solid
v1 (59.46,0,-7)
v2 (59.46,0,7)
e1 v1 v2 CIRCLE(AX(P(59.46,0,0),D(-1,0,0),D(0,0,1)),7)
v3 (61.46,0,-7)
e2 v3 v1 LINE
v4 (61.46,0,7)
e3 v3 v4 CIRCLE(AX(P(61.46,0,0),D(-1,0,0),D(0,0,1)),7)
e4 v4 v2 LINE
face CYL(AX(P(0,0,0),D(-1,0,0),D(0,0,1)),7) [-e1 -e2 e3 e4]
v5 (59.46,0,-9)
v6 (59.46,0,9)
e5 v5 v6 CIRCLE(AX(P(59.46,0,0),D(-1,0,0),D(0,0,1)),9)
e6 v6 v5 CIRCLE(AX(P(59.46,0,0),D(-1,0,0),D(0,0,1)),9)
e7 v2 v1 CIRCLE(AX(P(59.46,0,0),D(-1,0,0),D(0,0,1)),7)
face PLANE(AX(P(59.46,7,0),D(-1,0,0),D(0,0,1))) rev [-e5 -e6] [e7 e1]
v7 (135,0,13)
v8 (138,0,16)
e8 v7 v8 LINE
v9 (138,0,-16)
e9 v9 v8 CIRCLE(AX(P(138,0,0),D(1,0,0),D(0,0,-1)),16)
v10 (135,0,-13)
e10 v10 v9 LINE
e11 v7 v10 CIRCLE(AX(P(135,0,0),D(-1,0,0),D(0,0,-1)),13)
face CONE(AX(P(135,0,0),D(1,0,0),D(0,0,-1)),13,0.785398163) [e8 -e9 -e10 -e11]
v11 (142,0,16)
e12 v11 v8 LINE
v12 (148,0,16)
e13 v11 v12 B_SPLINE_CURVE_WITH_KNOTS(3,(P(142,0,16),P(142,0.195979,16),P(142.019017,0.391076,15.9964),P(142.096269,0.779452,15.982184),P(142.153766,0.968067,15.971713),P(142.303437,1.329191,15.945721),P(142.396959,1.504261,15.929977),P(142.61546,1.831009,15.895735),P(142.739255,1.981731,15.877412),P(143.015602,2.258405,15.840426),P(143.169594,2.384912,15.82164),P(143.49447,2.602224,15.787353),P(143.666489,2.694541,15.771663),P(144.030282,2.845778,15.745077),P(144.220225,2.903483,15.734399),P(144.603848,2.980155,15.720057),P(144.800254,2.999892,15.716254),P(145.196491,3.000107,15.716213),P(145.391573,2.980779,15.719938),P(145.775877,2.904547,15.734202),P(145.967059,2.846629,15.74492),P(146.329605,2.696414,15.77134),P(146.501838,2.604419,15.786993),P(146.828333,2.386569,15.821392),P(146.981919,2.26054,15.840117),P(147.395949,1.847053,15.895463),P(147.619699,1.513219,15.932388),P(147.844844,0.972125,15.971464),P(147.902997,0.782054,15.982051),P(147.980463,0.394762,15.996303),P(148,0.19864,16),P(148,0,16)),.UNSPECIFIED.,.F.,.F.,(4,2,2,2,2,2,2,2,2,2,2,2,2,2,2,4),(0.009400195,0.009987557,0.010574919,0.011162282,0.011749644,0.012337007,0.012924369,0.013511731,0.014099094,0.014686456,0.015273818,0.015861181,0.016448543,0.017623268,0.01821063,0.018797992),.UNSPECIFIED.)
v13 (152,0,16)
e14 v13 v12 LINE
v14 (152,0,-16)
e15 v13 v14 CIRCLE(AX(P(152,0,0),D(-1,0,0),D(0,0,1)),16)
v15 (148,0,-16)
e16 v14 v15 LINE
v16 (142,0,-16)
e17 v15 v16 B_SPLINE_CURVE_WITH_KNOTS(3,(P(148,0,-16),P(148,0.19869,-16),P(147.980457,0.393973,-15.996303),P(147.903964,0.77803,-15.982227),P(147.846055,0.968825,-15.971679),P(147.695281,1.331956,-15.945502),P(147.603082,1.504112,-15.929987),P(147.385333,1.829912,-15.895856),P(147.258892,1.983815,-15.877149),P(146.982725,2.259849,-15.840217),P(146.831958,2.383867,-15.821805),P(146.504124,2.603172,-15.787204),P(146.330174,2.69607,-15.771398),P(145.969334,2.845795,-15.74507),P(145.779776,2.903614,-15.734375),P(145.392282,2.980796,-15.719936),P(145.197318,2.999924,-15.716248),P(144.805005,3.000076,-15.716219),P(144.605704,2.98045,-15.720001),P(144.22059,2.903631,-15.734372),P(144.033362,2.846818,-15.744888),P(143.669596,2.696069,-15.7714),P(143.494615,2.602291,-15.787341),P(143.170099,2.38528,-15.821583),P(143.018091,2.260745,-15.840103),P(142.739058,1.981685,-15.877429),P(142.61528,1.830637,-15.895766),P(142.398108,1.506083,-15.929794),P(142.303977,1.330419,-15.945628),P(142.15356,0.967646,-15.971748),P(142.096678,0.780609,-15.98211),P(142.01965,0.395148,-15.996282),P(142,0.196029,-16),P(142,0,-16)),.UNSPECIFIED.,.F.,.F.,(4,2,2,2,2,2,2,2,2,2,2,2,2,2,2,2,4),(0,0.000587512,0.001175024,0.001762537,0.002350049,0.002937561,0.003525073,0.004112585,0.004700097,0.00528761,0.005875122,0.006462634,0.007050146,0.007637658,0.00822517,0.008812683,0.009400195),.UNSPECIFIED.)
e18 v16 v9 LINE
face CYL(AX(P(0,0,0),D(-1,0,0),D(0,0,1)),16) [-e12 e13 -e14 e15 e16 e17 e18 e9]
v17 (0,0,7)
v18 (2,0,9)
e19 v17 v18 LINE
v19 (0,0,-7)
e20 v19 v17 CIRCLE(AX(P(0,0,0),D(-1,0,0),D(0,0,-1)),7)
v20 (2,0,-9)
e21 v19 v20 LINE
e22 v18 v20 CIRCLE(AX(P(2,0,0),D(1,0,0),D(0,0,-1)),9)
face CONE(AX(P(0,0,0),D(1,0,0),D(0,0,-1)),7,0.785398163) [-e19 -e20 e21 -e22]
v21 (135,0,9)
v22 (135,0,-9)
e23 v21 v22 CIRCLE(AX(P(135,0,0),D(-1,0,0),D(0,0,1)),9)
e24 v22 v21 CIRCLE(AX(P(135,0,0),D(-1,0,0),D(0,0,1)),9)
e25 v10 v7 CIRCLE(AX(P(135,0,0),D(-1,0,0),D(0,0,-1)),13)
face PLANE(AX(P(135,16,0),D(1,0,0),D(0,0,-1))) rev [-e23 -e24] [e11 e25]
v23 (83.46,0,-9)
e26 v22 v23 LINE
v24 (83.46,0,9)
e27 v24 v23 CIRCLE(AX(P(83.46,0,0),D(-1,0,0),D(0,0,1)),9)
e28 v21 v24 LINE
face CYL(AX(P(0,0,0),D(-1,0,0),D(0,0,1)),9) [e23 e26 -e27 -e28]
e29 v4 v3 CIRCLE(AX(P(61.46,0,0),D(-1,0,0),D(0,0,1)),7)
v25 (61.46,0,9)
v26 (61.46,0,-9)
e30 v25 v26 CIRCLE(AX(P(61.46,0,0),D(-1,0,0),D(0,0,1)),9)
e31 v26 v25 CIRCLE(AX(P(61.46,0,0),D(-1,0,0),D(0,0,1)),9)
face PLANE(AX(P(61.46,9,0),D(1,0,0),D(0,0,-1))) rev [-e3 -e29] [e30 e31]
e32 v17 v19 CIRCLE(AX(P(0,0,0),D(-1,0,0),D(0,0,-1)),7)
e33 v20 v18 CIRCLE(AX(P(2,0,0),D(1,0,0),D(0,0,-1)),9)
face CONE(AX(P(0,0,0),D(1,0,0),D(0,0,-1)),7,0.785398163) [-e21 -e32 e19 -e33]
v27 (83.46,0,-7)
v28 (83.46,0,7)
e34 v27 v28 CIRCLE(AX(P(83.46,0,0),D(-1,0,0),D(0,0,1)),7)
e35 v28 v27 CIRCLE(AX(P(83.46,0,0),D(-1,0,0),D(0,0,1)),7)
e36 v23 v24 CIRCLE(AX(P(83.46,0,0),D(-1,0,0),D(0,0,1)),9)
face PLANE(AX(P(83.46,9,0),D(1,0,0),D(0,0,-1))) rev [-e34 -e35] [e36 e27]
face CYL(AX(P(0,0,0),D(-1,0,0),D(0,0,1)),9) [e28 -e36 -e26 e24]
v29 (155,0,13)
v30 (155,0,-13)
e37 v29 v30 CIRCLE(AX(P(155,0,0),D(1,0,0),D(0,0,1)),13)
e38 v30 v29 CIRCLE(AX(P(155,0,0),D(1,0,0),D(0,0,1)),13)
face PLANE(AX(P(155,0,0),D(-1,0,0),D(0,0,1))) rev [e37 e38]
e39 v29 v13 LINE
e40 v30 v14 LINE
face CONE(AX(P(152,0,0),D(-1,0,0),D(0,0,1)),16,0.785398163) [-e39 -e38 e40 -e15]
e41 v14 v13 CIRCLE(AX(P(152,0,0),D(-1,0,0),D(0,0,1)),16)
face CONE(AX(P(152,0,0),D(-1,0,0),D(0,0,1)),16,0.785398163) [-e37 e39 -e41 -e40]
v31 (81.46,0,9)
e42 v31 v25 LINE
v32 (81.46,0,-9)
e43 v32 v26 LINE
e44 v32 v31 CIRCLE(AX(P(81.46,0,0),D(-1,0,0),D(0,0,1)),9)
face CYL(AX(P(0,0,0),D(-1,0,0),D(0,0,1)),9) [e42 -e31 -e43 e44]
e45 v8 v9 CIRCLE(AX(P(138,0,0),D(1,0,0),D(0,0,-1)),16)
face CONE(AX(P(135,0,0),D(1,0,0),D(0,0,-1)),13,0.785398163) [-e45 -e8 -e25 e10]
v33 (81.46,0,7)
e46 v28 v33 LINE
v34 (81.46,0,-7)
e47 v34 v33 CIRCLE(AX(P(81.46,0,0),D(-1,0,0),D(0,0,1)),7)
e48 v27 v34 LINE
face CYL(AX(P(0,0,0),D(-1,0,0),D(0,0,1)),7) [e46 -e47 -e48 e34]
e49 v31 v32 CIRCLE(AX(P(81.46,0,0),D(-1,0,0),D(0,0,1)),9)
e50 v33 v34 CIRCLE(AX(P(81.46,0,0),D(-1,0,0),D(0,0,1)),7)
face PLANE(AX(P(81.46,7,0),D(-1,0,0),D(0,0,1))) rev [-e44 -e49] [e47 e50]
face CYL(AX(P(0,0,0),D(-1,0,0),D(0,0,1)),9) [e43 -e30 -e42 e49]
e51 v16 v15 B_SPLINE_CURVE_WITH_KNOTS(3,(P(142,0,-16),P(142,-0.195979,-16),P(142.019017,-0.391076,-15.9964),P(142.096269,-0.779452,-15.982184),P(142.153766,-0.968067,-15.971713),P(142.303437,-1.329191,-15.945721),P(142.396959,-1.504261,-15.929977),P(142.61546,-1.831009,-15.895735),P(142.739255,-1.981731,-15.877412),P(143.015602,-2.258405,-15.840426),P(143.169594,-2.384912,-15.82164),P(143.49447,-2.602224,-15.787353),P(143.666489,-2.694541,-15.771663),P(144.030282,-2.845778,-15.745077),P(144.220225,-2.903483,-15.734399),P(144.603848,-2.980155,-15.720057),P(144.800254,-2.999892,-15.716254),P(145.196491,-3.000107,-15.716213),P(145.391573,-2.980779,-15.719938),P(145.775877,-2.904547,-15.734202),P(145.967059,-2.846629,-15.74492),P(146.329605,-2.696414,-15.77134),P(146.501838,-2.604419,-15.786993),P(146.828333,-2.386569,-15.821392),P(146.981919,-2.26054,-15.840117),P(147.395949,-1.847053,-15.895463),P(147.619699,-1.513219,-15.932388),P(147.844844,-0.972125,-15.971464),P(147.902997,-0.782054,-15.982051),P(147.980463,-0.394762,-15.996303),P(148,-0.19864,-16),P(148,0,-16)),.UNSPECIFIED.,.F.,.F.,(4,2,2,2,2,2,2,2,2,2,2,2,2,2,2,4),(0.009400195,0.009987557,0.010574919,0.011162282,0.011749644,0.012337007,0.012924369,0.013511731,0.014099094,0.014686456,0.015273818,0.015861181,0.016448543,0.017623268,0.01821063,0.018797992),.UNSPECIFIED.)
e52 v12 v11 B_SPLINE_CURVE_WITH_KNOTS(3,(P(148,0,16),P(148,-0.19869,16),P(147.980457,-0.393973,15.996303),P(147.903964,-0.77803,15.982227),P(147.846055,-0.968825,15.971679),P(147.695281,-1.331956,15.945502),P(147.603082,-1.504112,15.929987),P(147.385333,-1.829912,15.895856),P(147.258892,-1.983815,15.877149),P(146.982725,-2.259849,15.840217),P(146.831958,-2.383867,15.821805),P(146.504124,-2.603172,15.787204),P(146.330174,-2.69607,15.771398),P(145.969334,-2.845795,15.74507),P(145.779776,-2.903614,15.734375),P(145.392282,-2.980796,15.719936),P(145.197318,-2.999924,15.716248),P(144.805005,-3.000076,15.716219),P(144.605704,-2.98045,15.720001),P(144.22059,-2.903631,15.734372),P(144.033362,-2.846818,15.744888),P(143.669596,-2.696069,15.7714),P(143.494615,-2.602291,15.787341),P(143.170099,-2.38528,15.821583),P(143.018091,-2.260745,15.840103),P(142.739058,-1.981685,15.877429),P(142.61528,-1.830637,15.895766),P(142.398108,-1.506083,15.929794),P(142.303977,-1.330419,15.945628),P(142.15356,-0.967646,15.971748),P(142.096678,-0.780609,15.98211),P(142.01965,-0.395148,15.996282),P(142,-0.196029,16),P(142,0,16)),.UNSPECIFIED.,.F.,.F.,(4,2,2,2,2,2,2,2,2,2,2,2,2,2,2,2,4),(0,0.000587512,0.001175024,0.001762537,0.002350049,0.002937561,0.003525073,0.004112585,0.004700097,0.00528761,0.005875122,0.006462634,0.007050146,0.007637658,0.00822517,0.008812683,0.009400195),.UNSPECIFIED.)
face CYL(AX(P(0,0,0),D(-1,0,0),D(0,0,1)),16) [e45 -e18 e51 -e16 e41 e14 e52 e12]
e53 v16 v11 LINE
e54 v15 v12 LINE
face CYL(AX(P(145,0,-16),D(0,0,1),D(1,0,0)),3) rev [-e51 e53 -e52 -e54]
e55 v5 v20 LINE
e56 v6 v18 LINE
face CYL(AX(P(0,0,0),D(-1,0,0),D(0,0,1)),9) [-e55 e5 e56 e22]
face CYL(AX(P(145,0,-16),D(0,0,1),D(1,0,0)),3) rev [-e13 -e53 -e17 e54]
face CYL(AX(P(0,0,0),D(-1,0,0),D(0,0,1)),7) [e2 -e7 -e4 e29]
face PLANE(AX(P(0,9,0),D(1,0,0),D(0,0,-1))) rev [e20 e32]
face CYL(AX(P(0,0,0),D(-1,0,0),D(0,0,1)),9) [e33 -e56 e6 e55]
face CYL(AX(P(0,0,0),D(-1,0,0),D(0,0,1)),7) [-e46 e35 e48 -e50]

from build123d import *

# Parameters (mm, degrees)
HEAD_CHAMFER_3MM_SIZE      = 3
EDGE_CHAMFER_2MM_SIZE      = 2
HEAD_CROSS_HOLE_DEPTH      = 157.642906
HEAD_CROSS_HOLE_DEPTH_BACK = 157.642906
CROSS_HOLE_SKETCH_R        = 3


with BuildPart() as part:
    # Bolt Profile Sketch → Bolt Body Revolve (revolve)
    with BuildSketch(Plane.XY, mode=Mode.PRIVATE) as bolt_body_revolve_sk:
        Polygon((155, 0), (155, 16), (135, 16), (135, 9), (83.46, 9), (83.46, 7), (81.46, 7), (81.46, 9), (61.46, 9), (61.46, 7), (59.46, 7), (59.46, 9), (0, 9), (0, 0), align=None)
    revolve(bolt_body_revolve_sk.sketch.rotate(Axis((0, 0, 0), (1, 0, 0)), 90), axis=Axis((0, 0, 0), (1, 0, 0)))

    # Head Chamfer 3mm
    head_chamfer_3mm_edges = [part.edges().sort_by_distance(p)[0] for p in [
        (135, 0, -16),
        (155, 0, -16),
    ]]
    chamfer(head_chamfer_3mm_edges, length=HEAD_CHAMFER_3MM_SIZE)

    # Edge Chamfer 2mm
    edge_chamfer_2mm_edges = [part.edges().sort_by_distance(p)[0] for p in [
        (0, 0, -9),
    ]]
    chamfer(edge_chamfer_2mm_edges, length=EDGE_CHAMFER_2MM_SIZE)

    # Cross Hole Sketch → Head Cross Hole (cut, two sides: drawn at the far end of the back side and taken through both)
    with BuildSketch(Plane.XY.offset(-HEAD_CROSS_HOLE_DEPTH_BACK)):
        with Locations((145, 0)):
            Circle(CROSS_HOLE_SKETCH_R)
    extrude(amount=HEAD_CROSS_HOLE_DEPTH + HEAD_CROSS_HOLE_DEPTH_BACK, mode=Mode.SUBTRACT)


solid = part.part
